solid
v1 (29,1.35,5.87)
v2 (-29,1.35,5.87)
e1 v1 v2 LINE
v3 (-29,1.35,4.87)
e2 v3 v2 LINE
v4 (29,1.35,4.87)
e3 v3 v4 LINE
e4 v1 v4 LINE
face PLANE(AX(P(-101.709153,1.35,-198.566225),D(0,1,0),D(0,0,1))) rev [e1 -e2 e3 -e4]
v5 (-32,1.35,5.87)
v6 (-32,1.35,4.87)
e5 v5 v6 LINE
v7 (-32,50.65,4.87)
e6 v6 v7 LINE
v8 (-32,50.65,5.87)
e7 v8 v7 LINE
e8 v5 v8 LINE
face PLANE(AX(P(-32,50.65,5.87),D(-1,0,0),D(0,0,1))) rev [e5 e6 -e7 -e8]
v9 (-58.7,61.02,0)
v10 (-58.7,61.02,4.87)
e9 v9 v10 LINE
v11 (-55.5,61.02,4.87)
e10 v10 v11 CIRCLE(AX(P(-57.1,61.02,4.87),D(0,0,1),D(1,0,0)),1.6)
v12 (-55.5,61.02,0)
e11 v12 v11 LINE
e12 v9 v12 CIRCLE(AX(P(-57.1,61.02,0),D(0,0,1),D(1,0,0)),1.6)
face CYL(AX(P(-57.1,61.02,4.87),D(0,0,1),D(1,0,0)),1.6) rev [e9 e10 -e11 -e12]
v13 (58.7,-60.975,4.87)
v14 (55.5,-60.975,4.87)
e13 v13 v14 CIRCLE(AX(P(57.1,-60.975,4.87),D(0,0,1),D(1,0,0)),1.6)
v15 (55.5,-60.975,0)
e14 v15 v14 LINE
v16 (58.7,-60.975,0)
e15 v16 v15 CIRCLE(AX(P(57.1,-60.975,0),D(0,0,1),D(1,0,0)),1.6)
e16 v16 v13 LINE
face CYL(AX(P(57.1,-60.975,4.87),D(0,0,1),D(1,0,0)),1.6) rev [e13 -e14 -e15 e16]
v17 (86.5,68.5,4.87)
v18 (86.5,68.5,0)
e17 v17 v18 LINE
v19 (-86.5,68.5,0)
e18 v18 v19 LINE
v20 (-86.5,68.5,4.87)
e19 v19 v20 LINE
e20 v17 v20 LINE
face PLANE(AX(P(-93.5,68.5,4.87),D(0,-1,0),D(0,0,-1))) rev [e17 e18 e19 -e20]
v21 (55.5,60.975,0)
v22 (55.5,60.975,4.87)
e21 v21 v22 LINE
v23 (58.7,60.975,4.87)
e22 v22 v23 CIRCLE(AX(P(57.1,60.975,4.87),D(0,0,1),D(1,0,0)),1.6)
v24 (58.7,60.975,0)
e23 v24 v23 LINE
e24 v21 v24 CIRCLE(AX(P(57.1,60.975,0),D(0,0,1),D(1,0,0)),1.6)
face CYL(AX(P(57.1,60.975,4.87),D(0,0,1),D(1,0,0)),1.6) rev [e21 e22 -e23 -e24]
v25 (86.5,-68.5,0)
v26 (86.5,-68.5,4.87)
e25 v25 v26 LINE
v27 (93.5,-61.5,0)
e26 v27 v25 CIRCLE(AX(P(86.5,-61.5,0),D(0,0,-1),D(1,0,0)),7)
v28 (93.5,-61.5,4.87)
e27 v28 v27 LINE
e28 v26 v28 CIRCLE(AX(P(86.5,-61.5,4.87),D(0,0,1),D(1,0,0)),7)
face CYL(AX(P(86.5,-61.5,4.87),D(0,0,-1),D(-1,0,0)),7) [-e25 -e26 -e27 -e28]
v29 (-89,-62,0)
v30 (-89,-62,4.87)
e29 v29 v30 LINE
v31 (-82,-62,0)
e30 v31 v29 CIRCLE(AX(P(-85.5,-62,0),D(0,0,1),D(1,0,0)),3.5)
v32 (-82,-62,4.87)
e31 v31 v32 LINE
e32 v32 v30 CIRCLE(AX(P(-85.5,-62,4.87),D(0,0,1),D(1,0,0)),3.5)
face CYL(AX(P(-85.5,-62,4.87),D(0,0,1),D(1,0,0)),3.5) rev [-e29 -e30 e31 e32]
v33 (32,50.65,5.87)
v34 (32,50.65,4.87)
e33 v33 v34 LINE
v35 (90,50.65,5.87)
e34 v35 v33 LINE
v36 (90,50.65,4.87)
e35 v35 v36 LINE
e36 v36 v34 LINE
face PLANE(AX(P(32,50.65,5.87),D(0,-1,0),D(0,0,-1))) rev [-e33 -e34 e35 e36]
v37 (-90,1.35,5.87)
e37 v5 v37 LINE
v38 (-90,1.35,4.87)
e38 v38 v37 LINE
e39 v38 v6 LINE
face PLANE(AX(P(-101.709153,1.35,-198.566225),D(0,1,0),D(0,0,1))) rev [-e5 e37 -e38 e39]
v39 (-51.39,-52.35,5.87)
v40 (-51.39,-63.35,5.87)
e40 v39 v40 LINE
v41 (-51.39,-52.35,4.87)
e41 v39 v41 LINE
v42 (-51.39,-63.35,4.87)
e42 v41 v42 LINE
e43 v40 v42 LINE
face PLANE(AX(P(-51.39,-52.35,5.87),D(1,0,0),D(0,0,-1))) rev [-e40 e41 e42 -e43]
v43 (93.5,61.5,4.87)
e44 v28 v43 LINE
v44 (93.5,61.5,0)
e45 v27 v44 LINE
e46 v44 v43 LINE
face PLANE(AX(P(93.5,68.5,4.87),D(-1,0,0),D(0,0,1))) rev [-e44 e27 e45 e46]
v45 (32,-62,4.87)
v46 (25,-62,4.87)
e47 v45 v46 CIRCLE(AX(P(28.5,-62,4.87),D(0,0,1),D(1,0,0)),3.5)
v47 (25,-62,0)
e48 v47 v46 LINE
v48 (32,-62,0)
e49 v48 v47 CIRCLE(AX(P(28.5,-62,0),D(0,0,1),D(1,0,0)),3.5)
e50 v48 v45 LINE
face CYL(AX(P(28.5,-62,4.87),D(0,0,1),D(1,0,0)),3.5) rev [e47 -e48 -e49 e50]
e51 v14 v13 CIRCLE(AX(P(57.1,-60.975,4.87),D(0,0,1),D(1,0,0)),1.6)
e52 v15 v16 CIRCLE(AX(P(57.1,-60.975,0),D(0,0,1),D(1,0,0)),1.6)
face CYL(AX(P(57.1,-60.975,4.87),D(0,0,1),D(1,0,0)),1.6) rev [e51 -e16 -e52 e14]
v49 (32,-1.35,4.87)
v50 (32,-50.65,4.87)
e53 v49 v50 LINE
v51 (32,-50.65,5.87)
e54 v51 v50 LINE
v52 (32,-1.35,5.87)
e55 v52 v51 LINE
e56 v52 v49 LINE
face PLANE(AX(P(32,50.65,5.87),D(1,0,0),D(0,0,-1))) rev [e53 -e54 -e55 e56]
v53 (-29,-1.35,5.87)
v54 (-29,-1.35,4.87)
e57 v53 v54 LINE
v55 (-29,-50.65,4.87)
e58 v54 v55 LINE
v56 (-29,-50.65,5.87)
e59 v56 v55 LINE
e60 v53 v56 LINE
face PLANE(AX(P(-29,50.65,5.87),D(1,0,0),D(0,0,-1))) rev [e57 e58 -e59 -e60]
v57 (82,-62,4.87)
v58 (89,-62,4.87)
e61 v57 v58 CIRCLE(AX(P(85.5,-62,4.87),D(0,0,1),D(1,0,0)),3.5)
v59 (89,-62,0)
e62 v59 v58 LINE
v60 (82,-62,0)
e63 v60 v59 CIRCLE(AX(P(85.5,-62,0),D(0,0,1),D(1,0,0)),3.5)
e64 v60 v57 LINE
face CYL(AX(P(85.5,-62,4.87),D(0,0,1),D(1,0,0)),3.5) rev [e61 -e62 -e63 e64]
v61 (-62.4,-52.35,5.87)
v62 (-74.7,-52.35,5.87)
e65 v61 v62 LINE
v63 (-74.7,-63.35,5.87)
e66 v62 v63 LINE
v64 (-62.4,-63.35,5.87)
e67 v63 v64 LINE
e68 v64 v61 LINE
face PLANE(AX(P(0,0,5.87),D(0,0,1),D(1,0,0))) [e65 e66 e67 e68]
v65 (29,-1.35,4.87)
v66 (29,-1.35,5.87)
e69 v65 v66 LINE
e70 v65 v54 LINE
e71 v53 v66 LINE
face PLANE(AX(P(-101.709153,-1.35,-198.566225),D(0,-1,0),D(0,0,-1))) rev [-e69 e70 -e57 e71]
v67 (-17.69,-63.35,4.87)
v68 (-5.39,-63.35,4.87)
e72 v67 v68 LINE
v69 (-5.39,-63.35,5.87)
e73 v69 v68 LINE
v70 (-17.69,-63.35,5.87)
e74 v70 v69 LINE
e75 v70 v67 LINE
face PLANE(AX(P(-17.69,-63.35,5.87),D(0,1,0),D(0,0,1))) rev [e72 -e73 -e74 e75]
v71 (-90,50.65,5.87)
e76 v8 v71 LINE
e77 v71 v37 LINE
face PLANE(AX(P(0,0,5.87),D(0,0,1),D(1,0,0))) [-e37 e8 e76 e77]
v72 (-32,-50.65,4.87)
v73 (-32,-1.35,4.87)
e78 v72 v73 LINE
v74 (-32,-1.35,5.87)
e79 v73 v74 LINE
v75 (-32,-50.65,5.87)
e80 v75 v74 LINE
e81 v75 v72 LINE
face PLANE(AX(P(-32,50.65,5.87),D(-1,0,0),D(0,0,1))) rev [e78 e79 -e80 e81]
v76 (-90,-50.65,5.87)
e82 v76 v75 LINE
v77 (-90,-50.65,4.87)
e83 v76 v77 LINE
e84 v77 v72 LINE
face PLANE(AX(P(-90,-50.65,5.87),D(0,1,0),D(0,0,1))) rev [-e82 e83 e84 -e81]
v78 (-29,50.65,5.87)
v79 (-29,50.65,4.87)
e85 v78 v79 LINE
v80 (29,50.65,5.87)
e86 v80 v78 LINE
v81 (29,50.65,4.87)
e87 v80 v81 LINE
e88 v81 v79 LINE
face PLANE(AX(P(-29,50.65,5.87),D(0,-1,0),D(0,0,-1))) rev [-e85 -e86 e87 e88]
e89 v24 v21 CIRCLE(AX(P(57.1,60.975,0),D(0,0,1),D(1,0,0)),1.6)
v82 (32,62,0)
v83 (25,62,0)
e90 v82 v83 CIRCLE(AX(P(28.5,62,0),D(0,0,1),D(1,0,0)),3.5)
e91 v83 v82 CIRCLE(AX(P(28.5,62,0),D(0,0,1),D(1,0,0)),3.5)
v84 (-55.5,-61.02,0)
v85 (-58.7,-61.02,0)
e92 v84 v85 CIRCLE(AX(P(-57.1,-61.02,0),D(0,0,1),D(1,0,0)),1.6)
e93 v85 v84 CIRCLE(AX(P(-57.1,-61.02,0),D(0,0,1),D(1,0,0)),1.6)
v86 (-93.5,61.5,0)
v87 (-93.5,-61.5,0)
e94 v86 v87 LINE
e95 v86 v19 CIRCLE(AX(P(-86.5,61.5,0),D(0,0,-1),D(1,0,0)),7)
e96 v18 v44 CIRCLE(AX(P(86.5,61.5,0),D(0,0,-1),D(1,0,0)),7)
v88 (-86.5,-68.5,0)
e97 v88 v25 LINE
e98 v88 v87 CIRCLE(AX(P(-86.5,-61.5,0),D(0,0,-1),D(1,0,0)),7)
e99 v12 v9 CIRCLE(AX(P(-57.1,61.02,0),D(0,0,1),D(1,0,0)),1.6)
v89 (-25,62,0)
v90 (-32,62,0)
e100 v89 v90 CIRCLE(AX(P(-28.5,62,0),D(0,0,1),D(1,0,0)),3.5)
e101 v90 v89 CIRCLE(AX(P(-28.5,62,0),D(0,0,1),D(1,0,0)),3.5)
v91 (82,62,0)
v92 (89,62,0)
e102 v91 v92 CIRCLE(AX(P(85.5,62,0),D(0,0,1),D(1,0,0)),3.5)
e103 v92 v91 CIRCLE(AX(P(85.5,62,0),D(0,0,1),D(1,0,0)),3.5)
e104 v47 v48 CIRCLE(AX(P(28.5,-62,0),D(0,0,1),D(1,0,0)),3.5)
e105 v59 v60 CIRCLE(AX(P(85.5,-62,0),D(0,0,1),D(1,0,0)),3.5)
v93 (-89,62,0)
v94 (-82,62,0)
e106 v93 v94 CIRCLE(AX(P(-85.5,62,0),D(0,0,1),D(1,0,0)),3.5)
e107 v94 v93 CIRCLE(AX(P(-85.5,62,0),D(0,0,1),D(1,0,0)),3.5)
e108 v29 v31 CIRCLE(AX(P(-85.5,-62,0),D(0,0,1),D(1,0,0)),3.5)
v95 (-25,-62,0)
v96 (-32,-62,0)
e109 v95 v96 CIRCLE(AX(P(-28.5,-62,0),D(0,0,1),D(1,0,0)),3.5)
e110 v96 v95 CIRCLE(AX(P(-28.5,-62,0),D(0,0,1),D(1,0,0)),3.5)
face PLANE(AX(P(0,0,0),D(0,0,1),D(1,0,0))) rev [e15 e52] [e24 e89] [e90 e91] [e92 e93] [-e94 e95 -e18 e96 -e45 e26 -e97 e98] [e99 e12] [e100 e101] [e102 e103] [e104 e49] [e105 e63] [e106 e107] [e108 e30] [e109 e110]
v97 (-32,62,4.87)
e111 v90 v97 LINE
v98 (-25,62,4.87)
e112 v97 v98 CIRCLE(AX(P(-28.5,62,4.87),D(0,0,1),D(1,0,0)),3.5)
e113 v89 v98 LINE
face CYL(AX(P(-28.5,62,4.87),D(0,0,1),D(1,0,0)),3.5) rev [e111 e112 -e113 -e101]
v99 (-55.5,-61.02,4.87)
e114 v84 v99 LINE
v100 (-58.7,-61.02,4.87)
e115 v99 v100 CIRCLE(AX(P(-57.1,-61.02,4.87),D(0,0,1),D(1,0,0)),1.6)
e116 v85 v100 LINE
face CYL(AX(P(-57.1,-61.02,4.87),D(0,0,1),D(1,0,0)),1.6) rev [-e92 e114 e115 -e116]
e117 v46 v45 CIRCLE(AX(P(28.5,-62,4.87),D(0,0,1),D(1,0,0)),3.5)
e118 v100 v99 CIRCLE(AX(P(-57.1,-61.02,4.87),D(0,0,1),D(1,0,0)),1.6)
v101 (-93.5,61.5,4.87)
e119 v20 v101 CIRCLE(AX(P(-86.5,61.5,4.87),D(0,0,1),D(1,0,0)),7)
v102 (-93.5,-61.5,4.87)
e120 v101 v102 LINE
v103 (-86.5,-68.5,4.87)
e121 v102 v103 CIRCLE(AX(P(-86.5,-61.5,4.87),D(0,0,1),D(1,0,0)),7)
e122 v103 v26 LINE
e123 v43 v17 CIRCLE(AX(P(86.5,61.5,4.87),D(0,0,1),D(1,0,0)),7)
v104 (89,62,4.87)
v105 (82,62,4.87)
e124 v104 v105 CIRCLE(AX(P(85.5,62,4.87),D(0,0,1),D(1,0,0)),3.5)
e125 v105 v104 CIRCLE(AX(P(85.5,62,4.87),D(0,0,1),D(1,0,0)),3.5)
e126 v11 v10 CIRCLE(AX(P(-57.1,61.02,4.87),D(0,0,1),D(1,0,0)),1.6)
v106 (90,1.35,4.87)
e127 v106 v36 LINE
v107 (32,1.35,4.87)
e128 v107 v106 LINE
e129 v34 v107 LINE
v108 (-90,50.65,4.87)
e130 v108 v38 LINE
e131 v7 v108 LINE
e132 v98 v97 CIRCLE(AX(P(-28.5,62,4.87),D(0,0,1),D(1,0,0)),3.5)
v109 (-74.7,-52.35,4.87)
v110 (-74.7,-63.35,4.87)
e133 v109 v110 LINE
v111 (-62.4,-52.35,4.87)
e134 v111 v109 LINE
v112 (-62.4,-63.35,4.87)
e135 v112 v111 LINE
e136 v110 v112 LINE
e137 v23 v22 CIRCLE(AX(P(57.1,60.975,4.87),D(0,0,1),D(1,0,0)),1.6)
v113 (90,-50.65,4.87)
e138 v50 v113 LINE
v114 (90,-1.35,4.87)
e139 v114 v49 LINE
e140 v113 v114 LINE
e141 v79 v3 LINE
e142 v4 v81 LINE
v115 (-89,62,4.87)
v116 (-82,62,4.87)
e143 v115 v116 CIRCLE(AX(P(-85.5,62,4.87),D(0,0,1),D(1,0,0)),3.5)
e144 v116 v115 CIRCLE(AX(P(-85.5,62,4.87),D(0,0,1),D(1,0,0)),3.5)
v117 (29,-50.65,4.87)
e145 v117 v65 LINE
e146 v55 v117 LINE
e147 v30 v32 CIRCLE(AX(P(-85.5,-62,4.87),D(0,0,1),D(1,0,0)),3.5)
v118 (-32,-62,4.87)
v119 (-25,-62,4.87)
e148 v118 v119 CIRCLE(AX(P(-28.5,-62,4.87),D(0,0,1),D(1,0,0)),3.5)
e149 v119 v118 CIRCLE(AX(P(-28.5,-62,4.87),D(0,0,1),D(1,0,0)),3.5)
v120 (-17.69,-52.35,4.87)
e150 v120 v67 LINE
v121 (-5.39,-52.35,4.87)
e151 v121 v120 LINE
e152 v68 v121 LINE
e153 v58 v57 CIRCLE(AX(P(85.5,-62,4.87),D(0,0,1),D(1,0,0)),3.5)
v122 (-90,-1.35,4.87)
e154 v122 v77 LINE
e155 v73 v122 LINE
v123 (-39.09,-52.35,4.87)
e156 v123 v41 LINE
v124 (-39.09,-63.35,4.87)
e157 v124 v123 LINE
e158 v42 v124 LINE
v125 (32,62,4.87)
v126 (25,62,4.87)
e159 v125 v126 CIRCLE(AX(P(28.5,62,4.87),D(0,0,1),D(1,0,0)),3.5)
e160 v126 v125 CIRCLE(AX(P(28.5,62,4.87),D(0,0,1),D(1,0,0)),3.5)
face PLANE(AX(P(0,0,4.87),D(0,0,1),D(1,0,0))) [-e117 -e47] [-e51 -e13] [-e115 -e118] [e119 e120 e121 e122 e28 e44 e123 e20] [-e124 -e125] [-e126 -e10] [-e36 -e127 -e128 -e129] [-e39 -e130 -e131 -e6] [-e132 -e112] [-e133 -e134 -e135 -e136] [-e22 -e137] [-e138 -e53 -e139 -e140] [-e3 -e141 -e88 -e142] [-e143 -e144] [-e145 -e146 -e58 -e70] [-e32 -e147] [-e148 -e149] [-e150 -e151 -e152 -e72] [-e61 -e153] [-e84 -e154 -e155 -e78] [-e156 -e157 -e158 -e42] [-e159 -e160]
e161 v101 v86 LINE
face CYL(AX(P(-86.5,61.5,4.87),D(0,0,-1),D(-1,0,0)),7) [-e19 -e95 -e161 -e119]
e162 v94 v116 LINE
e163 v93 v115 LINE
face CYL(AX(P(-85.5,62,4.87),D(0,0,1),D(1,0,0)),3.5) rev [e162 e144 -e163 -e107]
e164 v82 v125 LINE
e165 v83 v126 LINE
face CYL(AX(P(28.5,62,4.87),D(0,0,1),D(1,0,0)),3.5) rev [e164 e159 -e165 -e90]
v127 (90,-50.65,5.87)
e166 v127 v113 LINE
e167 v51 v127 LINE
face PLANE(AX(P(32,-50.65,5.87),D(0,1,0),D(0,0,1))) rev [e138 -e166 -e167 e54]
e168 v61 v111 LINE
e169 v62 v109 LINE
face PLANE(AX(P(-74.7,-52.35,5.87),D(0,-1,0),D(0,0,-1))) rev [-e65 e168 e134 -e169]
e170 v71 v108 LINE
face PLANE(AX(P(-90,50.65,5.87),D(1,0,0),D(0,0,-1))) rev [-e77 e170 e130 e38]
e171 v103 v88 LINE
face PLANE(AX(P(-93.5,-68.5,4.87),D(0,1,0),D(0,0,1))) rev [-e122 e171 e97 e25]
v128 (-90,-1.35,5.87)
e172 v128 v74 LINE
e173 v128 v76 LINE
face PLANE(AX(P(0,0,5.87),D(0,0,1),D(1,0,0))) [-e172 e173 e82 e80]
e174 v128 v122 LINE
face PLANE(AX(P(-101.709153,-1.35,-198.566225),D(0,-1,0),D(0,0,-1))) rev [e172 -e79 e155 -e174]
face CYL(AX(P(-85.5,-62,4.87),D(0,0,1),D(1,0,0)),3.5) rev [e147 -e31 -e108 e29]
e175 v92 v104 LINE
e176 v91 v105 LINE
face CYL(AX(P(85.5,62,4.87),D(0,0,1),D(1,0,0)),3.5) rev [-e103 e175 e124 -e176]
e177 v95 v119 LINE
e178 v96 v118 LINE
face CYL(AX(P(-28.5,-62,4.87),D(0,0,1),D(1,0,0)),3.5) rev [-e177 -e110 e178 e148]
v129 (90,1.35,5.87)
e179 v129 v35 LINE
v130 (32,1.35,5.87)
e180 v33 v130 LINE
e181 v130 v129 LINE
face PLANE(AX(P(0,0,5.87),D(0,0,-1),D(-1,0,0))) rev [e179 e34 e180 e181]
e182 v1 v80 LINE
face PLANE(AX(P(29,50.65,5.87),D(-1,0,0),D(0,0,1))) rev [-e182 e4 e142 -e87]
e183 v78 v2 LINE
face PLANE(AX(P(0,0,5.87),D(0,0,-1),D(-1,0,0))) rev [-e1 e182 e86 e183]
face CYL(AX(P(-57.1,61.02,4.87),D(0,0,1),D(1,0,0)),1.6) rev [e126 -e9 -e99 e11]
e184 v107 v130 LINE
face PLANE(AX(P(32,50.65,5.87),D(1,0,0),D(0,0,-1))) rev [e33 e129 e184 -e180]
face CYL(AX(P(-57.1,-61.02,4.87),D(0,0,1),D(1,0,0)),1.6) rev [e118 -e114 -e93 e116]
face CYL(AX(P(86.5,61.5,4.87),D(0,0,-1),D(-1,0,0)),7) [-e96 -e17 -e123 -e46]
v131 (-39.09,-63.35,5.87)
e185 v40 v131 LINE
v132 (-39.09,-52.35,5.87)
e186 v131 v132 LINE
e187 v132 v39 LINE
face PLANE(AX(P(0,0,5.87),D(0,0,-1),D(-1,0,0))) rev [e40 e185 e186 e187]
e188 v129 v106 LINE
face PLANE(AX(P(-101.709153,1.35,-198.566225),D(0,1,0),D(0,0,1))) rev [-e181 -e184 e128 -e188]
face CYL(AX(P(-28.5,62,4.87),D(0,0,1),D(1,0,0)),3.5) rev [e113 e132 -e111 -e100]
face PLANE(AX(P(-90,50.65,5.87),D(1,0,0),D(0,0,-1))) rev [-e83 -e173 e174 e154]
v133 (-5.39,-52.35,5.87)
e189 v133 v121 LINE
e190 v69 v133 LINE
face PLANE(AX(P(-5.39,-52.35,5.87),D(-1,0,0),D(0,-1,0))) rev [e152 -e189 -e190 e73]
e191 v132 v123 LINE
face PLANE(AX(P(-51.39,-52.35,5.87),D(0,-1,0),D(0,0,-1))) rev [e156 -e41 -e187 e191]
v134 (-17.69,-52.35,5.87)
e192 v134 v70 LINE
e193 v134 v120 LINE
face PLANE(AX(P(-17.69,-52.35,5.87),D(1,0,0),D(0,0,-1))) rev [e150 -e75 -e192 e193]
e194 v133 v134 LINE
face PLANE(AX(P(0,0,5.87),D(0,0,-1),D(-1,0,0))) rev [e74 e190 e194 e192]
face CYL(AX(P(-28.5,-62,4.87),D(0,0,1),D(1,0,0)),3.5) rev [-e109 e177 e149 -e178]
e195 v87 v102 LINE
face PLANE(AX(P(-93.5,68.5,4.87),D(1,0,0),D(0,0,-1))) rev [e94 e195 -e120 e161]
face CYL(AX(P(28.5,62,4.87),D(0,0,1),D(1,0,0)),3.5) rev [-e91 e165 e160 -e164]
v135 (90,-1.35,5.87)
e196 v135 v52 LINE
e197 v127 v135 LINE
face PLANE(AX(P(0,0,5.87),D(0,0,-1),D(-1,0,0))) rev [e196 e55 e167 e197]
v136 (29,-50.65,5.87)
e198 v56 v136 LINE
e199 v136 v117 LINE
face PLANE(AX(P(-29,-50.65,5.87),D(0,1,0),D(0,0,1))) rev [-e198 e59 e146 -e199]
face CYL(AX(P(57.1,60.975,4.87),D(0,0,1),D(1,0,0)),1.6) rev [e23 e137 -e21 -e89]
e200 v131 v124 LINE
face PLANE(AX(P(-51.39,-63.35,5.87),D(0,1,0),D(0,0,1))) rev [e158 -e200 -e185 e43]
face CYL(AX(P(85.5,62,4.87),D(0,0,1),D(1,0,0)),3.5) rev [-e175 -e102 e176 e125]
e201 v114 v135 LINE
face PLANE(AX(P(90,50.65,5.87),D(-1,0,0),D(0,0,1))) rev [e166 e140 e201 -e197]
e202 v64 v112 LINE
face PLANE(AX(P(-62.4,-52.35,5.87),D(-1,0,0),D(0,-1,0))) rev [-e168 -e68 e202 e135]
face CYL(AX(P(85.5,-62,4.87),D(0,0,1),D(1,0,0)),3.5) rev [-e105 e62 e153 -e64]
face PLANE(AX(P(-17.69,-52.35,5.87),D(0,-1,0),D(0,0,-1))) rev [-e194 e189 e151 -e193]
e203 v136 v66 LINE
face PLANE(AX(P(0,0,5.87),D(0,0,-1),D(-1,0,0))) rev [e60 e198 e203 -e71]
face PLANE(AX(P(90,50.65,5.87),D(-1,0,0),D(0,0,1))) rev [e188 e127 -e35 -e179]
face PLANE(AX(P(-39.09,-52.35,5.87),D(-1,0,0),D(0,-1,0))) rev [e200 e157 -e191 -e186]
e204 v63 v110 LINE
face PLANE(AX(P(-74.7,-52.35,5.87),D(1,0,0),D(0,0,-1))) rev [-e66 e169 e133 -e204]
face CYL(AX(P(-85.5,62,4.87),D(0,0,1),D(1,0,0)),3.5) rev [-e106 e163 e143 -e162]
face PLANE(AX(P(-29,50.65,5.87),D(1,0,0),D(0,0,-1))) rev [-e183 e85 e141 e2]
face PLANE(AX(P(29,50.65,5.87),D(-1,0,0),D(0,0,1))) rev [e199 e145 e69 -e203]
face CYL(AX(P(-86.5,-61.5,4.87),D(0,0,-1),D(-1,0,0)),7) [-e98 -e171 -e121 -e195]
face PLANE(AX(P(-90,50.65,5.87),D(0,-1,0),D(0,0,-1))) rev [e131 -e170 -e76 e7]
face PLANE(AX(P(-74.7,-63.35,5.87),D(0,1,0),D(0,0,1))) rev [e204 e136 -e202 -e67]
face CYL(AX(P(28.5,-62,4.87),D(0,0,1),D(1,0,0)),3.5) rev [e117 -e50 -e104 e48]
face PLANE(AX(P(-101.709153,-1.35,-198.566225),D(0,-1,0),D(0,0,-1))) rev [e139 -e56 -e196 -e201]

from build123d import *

# Parameters (mm, degrees)
SKETCH1_W                  = 187
SKETCH1_H                  = 137
BOSS_EXTRUDE1_DEPTH        = 4.87
F_7_0_7_DIAMETER_HOLE1_D   = 7
F_3_2_3_2_DIAMETER_HOLE1_D = 3.2
SKETCH6_W                  = 58
SKETCH6_H                  = 101.3
BOSS_EXTRUDE2_DEPTH        = 1
SKETCH7_W                  = 12.3
SKETCH7_H                  = 11
BOSS_EXTRUDE3_DEPTH        = 1
SKETCH8_W                  = 203.41830683
SKETCH8_H                  = 2.7
CUT_EXTRUDE1_DEPTH         = 1
FILLET1_R                  = 7


with BuildPart() as part:
    # Sketch1 → Boss-Extrude1 (new body)
    with BuildSketch(Plane.XY):
        Rectangle(SKETCH1_W, SKETCH1_H)
    extrude(amount=BOSS_EXTRUDE1_DEPTH)

    # Ø7.0 (7) Diameter Hole1 (through all)
    with Locations(Plane.XY.offset(4.87)):
        with Locations((-28.5, 62), (-85.5, 62), (28.5, 62), (85.5, 62), (85.5, -62), (28.5, -62), (-85.5, -62), (-28.5, -62)):
            Hole(F_7_0_7_DIAMETER_HOLE1_D / 2)

    # Ø3.2 (3.2) Diameter Hole1 (through all)
    with Locations(Plane.XY.offset(4.87)):
        with Locations((-57.1, 61.02), (57.1, 60.975), (57.1, -60.975), (-57.1, -61.02)):
            Hole(F_3_2_3_2_DIAMETER_HOLE1_D / 2)

    # Sketch6 → Boss-Extrude2 (add)
    with BuildSketch(Plane.XY.offset(4.87)):
        with Locations((-61, 0)):
            Rectangle(SKETCH6_W, SKETCH6_H)
        Rectangle(SKETCH6_W, SKETCH6_H)
        with Locations((61, 0)):
            Rectangle(SKETCH6_W, SKETCH6_H)
    extrude(amount=BOSS_EXTRUDE2_DEPTH)

    # Sketch7 → Boss-Extrude3 (add)
    with BuildSketch(Plane.XY.offset(4.87)):
        with Locations((-68.55, -57.85)):
            Rectangle(SKETCH7_W, SKETCH7_H)
        with Locations((-45.24, -57.85)):
            Rectangle(SKETCH7_W, SKETCH7_H)
        with Locations((-11.54, -57.85)):
            Rectangle(SKETCH7_W, SKETCH7_H)
    extrude(amount=BOSS_EXTRUDE3_DEPTH)

    # Sketch8 → Cut-Extrude1 (cut)
    with BuildSketch(Plane.XY.offset(5.87)):
        Rectangle(SKETCH8_W, SKETCH8_H)
    extrude(amount=-CUT_EXTRUDE1_DEPTH, mode=Mode.SUBTRACT)

    # Fillet1
    fillet1_edges = [part.edges().sort_by_distance(p)[0] for p in [
        (93.5, -68.5, 2.435),
        (-93.5, -68.5, 2.435),
        (-93.5, 68.5, 2.435),
        (93.5, 68.5, 2.435),
    ]]
    fillet(fillet1_edges, radius=FILLET1_R)


solid = part.part
